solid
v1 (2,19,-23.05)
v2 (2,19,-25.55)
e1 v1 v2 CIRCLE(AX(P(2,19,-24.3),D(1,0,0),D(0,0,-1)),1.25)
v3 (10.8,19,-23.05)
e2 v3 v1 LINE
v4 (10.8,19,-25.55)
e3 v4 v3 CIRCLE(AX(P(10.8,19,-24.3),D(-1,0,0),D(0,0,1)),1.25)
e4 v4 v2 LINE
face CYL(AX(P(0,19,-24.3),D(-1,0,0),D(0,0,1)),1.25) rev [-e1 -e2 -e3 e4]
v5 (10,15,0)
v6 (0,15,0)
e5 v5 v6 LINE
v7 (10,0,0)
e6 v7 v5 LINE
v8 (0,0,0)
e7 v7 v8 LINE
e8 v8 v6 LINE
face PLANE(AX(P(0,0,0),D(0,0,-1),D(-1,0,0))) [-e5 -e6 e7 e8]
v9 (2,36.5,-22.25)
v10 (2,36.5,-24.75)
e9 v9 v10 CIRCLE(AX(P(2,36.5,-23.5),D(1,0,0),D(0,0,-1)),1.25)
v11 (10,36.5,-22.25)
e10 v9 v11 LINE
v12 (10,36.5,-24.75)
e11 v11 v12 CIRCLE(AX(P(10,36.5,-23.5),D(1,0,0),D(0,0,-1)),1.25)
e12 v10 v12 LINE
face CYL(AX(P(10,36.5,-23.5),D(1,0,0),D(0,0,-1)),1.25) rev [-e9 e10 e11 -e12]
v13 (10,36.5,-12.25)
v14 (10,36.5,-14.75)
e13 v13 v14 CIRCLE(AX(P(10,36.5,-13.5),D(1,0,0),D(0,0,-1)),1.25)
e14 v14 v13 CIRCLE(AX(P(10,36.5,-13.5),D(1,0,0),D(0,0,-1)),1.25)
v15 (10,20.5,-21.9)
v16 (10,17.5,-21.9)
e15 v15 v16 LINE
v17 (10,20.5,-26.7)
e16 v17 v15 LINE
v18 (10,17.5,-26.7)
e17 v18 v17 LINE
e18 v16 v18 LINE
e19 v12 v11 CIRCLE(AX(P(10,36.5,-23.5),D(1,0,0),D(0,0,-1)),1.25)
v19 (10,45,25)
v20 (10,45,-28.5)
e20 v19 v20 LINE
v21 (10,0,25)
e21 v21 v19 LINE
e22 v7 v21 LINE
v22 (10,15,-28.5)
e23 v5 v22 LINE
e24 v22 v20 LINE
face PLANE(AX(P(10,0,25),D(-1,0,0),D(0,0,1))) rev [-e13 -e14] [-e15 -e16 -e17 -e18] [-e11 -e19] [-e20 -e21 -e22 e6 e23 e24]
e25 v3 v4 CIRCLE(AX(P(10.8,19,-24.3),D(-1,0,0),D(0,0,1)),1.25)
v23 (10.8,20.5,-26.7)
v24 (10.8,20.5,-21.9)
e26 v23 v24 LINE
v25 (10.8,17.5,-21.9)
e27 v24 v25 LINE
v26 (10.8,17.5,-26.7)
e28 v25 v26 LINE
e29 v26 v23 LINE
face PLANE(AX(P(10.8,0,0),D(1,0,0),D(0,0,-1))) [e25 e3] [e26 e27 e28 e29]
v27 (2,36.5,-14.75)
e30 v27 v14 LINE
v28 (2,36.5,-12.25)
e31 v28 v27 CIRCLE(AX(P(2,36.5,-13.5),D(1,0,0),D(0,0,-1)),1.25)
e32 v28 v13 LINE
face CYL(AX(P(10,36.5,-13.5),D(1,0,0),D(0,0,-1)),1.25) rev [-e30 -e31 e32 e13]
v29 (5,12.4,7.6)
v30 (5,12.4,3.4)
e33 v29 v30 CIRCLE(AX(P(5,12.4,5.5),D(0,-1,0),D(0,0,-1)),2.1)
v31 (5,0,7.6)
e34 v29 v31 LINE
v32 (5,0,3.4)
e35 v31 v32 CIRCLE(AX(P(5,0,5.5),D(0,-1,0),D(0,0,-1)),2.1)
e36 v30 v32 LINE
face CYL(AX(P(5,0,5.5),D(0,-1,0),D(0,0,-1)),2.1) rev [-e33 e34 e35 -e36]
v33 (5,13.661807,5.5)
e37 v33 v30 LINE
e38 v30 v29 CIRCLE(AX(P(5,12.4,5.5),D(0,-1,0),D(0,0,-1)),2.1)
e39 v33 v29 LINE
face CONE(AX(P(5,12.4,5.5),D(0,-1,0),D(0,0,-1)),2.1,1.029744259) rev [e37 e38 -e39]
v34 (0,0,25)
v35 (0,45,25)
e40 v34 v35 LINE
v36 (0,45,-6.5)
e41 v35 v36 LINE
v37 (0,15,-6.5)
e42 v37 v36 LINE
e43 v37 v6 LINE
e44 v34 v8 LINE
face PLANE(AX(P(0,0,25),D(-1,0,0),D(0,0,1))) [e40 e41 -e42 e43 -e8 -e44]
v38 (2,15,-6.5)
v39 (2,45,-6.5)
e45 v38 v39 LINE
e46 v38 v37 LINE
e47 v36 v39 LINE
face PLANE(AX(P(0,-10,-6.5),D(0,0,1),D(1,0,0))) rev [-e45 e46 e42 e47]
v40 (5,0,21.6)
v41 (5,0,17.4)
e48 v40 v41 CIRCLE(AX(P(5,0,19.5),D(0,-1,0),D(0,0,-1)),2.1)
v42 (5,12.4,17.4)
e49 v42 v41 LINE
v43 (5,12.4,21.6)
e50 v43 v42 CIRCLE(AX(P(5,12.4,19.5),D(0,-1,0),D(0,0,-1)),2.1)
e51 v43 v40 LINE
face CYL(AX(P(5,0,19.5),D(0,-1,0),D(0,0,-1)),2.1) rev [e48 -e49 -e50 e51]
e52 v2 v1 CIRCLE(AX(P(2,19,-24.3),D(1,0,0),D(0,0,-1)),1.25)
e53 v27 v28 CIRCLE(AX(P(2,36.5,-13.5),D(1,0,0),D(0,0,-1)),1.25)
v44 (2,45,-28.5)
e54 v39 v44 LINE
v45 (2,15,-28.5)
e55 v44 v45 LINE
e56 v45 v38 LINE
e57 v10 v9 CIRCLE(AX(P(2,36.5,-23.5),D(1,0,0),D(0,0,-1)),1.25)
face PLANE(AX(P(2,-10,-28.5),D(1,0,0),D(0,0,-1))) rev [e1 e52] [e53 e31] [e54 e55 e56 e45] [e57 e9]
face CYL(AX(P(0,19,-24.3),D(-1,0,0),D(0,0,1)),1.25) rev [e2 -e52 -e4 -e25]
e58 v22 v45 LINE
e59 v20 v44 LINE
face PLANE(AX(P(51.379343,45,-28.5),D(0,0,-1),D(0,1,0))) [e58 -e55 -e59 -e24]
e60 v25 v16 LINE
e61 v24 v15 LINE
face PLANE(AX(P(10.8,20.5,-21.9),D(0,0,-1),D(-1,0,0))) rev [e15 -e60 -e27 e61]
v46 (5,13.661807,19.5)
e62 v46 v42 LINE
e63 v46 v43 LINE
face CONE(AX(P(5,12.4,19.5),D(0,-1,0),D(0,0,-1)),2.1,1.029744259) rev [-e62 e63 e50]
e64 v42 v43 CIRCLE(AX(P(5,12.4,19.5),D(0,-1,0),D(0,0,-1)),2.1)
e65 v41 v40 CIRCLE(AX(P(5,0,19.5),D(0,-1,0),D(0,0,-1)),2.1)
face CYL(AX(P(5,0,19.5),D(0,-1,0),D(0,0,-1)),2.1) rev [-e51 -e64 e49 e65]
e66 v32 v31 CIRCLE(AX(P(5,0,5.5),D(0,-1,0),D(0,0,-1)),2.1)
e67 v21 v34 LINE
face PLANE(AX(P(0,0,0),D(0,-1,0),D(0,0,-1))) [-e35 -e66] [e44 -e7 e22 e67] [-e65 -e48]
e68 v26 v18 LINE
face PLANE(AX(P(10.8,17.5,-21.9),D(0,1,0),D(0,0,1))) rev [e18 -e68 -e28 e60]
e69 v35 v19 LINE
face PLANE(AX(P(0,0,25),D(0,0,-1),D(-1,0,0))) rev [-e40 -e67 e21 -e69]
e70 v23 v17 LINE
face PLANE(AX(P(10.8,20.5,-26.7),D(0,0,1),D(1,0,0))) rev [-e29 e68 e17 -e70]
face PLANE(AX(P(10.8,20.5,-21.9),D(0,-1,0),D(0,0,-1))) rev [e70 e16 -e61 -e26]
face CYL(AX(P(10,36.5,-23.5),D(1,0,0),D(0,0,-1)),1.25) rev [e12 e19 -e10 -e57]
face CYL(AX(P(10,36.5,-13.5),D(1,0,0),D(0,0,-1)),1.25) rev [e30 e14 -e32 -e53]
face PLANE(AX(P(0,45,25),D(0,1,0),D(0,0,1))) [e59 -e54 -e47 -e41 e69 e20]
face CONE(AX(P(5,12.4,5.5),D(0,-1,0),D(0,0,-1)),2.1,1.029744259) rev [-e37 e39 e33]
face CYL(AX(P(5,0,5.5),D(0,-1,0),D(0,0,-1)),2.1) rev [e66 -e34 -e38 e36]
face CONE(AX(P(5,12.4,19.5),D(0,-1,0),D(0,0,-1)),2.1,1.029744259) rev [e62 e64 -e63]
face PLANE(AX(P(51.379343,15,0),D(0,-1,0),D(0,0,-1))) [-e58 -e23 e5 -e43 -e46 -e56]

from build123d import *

# Parameters (mm, degrees)
EXTRUDE_THIN1_DEPTH   = 25
SKETCH2_W             = 28.5
SKETCH2_H             = 30
BOSS_EXTRUDE1_DEPTH   = 10
SKETCH5_W             = 2
SKETCH5_H             = 22
CUT_EXTRUDE1_DEPTH    = 64.735782728
M3_TAPPED_HOLE2_D     = 2.5
SKETCH8_W             = 85.55195354
SKETCH8_H             = 65.589831047
CUT_EXTRUDE2_DEPTH    = 10
M5_TAPPED_HOLE1_D     = 4.2
M5_TAPPED_HOLE1_DEPTH = 12.4
M5_TAPPED_HOLE1_TIP   = 1.2618073
SKETCH14_W            = 4.8
SKETCH14_H            = 3
BOSS_EXTRUDE2_DEPTH   = 0.8
M3_TAPPED_HOLE1_D     = 2.5


with BuildPart() as part:
    # Sketch1 → Extrude-Thin1 (new body)
    with BuildSketch(Plane.XY):
        Polygon((-15, 0), (0, 0), (0, 45), (10, 45), (10, -10), (-15, -10), align=None)
    extrude(amount=EXTRUDE_THIN1_DEPTH)

    # Sketch2 → Boss-Extrude1 (add)
    with BuildSketch(Plane.ZY):
        with Locations((-14.25, 30)):
            Rectangle(SKETCH2_W, SKETCH2_H)
    extrude(amount=-BOSS_EXTRUDE1_DEPTH)

    # Sketch5 → Cut-Extrude1 (cut, through all)
    with BuildSketch(Plane(origin=(0, 45, 0), x_dir=(1, 0, 0), z_dir=(0, 1, 0))):
        with Locations((1, 17.5)):
            Rectangle(SKETCH5_W, SKETCH5_H)
    extrude(amount=-CUT_EXTRUDE1_DEPTH, mode=Mode.SUBTRACT)

    # M3 Tapped Hole2 (through all)
    with Locations(Plane(origin=(10, 0, 0), x_dir=(0, 0, -1), z_dir=(1, 0, 0))):
        with Locations((13.5, 36.5), (23.5, 36.5)):
            Hole(M3_TAPPED_HOLE2_D / 2)

    # Sketch8 → Cut-Extrude2 (cut)
    with BuildSketch(Plane.XZ.offset(10)):
        with Locations((-7.814591053, 5.120081117)):
            Rectangle(SKETCH8_W, SKETCH8_H)
    extrude(amount=-CUT_EXTRUDE2_DEPTH, mode=Mode.SUBTRACT)

    # M5 Tapped Hole1
    with Locations(Plane(origin=(0, 0, 0), x_dir=(-1, 0, 0), z_dir=(0, -1, 0))):
        with Locations((-5, -5.5), (-5, -19.5)):
            Hole(M5_TAPPED_HOLE1_D / 2, depth=M5_TAPPED_HOLE1_DEPTH)
            with Locations((0, 0, -(M5_TAPPED_HOLE1_DEPTH + M5_TAPPED_HOLE1_TIP / 2))):  # 118° drill point
                Cone(0, M5_TAPPED_HOLE1_D / 2, M5_TAPPED_HOLE1_TIP, mode=Mode.SUBTRACT)

    # Sketch14 → Boss-Extrude2 (add)
    with BuildSketch(Plane(origin=(10, 0, 0), x_dir=(0, 0, -1), z_dir=(1, 0, 0))):
        with Locations((24.3, 19)):
            Rectangle(SKETCH14_W, SKETCH14_H)
    extrude(amount=BOSS_EXTRUDE2_DEPTH)

    # M3 Tapped Hole1 (through all)
    with Locations(Plane.ZY):
        with Locations((-24.3, 19)):
            Hole(M3_TAPPED_HOLE1_D / 2)


solid = part.part
